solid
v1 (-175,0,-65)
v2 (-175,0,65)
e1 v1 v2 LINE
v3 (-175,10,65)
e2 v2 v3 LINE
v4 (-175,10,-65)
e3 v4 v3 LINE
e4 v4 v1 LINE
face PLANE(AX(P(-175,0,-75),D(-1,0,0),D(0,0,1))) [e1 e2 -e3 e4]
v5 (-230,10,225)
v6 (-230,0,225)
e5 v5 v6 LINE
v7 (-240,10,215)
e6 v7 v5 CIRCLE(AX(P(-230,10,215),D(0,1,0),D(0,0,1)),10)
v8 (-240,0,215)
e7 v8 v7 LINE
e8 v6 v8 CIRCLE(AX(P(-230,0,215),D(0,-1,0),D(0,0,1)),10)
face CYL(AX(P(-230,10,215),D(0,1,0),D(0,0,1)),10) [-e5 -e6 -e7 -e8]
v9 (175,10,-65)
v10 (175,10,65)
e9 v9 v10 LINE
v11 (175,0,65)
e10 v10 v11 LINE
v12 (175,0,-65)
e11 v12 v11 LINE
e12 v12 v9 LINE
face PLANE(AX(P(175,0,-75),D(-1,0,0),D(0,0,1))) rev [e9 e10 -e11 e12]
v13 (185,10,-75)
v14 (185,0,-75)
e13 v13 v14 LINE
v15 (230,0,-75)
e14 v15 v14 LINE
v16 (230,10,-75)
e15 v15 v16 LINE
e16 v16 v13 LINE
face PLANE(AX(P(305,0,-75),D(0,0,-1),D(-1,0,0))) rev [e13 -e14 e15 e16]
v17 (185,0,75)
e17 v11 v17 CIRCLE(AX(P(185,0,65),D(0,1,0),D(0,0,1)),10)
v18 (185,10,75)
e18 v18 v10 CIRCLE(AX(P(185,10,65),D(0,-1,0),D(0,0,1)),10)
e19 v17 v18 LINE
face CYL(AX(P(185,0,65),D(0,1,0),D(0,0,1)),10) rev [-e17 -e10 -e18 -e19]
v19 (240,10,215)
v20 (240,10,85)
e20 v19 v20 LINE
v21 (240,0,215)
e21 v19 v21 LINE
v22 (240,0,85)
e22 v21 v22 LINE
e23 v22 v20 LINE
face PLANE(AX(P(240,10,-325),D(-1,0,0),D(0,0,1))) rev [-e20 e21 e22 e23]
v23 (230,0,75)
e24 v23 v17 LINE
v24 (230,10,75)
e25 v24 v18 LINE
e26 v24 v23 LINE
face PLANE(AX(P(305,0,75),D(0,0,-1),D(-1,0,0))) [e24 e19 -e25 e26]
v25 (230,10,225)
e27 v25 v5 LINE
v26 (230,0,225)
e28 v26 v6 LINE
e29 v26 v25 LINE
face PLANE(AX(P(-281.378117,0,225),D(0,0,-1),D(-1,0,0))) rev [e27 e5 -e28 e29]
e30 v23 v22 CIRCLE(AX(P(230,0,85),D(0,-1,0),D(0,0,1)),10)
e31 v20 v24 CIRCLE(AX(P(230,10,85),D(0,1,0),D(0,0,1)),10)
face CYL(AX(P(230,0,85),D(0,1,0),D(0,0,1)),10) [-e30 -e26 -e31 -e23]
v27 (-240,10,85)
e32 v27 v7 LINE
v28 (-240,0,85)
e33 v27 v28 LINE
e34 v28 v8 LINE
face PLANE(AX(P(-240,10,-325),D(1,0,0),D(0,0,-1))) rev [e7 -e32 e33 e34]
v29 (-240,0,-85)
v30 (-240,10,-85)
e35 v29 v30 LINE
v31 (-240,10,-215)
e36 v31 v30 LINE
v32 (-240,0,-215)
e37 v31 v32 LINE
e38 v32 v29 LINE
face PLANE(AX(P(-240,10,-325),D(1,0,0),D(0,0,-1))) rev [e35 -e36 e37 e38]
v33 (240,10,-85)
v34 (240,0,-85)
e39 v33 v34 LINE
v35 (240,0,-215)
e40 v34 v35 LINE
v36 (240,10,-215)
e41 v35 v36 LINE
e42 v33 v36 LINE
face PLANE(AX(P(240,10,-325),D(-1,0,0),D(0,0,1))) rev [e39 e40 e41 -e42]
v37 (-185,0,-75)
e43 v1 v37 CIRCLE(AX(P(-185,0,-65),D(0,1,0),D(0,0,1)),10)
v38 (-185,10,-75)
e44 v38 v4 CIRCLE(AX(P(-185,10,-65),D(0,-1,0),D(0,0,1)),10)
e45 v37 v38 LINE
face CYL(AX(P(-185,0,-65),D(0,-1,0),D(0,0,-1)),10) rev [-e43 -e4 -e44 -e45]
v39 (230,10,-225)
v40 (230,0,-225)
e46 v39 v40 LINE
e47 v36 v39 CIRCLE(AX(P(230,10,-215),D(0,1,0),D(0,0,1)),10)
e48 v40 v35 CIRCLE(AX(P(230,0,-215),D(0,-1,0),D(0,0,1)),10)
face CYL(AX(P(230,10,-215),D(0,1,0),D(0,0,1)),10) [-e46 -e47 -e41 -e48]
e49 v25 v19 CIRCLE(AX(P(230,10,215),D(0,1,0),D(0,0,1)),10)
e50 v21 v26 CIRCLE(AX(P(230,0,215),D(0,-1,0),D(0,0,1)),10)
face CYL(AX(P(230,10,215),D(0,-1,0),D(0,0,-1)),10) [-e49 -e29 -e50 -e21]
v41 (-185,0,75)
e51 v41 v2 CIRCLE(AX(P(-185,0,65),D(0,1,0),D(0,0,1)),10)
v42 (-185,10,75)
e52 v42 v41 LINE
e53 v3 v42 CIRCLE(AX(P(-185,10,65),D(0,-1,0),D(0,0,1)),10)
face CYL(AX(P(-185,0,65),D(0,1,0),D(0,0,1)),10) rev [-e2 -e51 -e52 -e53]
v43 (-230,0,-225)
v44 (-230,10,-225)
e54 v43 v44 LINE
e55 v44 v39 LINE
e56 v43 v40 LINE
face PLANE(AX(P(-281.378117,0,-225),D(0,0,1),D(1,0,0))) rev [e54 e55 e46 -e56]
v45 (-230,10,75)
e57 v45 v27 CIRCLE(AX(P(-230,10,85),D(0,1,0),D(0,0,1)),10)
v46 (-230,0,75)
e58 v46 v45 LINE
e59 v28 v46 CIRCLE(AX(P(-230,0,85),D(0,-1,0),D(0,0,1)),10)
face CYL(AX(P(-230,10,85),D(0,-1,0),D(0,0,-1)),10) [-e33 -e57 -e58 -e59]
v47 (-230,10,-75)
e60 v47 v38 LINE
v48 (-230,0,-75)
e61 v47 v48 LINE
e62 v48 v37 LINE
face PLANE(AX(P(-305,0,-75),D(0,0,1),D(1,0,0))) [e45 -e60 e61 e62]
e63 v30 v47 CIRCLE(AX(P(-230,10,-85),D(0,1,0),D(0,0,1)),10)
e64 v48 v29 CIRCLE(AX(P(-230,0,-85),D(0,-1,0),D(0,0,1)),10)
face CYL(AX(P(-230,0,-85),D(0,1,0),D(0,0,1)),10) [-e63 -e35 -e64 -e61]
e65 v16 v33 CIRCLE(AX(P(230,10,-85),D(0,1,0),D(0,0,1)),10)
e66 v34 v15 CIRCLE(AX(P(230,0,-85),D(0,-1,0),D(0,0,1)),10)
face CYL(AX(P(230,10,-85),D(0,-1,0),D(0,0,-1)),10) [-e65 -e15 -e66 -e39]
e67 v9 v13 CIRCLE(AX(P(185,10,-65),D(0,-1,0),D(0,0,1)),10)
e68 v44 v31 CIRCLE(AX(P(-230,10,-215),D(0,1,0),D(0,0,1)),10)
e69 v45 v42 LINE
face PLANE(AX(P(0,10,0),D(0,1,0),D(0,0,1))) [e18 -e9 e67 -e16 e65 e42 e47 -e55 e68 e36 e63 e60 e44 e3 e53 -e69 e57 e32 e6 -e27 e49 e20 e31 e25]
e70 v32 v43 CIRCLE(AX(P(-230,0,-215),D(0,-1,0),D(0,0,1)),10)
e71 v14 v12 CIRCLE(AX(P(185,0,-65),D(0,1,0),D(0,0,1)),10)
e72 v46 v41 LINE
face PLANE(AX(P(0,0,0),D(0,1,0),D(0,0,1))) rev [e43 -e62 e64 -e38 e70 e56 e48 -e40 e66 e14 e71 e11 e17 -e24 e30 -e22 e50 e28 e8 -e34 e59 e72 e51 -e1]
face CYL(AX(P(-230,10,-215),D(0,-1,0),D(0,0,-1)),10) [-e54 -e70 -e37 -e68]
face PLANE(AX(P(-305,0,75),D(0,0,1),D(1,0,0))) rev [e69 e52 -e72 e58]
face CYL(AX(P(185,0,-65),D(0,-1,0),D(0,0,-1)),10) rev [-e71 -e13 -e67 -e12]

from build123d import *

# Parameters (mm, degrees)
SKETCH1_W           = 480
SKETCH1_H           = 650
BOSS_EXTRUDE1_DEPTH = 10
FILLET2_R           = 60
SKETCH3_W           = 130
SKETCH3_H           = 150
CUT_EXTRUDE1_DEPTH  = 10
SKETCH5_W           = 562.756234426
SKETCH5_H           = 100
CUT_EXTRUDE2_DEPTH  = 10
FILLET3_R           = 10


with BuildPart() as part:
    # Sketch1 → Boss-Extrude1 (new body)
    with BuildSketch(Plane(origin=(0, 0, 0), x_dir=(1, 0, 0), z_dir=(0, 1, 0))):
        Rectangle(SKETCH1_W, SKETCH1_H)
    extrude(amount=BOSS_EXTRUDE1_DEPTH)

    # Fillet2
    fillet2_edges = [part.edges().sort_by_distance(p)[0] for p in [
        (240, 5, 325),
        (-240, 5, 325),
        (-240, 5, -325),
        (240, 5, -325),
    ]]
    fillet(fillet2_edges, radius=FILLET2_R)

    # Sketch3 → Cut-Extrude1 (cut)
    with BuildSketch(Plane(origin=(0, 10, 0), x_dir=(1, 0, 0), z_dir=(0, 1, 0))):
        with Locations((240, 0)):
            Rectangle(SKETCH3_W, SKETCH3_H)
        with Locations((-240, 0)):
            Rectangle(SKETCH3_W, SKETCH3_H)
    extrude(amount=-CUT_EXTRUDE1_DEPTH, mode=Mode.SUBTRACT)

    # Sketch5 → Cut-Extrude2 (cut)
    with BuildSketch(Plane(origin=(0, 10, 0), x_dir=(1, 0, 0), z_dir=(0, 1, 0))):
        with Locations((0, -275)):
            Rectangle(SKETCH5_W, SKETCH5_H)
        with Locations((0, 275)):
            Rectangle(SKETCH5_W, SKETCH5_H)
    extrude(amount=-CUT_EXTRUDE2_DEPTH, mode=Mode.SUBTRACT)

    # Fillet3
    fillet3_edges = [part.edges().sort_by_distance(p)[0] for p in [
        (-240, 5, 75),
        (-175, 5, 75),
        (-240, 5, -75),
        (-175, 5, -75),
        (240, 5, -75),
        (175, 5, -75),
        (240, 5, 75),
        (175, 5, 75),
        (-240, 5, 225),
        (240, 5, -225),
        (240, 5, 225),
        (-240, 5, -225),
    ]]
    fillet(fillet3_edges, radius=FILLET3_R)


solid = part.part
